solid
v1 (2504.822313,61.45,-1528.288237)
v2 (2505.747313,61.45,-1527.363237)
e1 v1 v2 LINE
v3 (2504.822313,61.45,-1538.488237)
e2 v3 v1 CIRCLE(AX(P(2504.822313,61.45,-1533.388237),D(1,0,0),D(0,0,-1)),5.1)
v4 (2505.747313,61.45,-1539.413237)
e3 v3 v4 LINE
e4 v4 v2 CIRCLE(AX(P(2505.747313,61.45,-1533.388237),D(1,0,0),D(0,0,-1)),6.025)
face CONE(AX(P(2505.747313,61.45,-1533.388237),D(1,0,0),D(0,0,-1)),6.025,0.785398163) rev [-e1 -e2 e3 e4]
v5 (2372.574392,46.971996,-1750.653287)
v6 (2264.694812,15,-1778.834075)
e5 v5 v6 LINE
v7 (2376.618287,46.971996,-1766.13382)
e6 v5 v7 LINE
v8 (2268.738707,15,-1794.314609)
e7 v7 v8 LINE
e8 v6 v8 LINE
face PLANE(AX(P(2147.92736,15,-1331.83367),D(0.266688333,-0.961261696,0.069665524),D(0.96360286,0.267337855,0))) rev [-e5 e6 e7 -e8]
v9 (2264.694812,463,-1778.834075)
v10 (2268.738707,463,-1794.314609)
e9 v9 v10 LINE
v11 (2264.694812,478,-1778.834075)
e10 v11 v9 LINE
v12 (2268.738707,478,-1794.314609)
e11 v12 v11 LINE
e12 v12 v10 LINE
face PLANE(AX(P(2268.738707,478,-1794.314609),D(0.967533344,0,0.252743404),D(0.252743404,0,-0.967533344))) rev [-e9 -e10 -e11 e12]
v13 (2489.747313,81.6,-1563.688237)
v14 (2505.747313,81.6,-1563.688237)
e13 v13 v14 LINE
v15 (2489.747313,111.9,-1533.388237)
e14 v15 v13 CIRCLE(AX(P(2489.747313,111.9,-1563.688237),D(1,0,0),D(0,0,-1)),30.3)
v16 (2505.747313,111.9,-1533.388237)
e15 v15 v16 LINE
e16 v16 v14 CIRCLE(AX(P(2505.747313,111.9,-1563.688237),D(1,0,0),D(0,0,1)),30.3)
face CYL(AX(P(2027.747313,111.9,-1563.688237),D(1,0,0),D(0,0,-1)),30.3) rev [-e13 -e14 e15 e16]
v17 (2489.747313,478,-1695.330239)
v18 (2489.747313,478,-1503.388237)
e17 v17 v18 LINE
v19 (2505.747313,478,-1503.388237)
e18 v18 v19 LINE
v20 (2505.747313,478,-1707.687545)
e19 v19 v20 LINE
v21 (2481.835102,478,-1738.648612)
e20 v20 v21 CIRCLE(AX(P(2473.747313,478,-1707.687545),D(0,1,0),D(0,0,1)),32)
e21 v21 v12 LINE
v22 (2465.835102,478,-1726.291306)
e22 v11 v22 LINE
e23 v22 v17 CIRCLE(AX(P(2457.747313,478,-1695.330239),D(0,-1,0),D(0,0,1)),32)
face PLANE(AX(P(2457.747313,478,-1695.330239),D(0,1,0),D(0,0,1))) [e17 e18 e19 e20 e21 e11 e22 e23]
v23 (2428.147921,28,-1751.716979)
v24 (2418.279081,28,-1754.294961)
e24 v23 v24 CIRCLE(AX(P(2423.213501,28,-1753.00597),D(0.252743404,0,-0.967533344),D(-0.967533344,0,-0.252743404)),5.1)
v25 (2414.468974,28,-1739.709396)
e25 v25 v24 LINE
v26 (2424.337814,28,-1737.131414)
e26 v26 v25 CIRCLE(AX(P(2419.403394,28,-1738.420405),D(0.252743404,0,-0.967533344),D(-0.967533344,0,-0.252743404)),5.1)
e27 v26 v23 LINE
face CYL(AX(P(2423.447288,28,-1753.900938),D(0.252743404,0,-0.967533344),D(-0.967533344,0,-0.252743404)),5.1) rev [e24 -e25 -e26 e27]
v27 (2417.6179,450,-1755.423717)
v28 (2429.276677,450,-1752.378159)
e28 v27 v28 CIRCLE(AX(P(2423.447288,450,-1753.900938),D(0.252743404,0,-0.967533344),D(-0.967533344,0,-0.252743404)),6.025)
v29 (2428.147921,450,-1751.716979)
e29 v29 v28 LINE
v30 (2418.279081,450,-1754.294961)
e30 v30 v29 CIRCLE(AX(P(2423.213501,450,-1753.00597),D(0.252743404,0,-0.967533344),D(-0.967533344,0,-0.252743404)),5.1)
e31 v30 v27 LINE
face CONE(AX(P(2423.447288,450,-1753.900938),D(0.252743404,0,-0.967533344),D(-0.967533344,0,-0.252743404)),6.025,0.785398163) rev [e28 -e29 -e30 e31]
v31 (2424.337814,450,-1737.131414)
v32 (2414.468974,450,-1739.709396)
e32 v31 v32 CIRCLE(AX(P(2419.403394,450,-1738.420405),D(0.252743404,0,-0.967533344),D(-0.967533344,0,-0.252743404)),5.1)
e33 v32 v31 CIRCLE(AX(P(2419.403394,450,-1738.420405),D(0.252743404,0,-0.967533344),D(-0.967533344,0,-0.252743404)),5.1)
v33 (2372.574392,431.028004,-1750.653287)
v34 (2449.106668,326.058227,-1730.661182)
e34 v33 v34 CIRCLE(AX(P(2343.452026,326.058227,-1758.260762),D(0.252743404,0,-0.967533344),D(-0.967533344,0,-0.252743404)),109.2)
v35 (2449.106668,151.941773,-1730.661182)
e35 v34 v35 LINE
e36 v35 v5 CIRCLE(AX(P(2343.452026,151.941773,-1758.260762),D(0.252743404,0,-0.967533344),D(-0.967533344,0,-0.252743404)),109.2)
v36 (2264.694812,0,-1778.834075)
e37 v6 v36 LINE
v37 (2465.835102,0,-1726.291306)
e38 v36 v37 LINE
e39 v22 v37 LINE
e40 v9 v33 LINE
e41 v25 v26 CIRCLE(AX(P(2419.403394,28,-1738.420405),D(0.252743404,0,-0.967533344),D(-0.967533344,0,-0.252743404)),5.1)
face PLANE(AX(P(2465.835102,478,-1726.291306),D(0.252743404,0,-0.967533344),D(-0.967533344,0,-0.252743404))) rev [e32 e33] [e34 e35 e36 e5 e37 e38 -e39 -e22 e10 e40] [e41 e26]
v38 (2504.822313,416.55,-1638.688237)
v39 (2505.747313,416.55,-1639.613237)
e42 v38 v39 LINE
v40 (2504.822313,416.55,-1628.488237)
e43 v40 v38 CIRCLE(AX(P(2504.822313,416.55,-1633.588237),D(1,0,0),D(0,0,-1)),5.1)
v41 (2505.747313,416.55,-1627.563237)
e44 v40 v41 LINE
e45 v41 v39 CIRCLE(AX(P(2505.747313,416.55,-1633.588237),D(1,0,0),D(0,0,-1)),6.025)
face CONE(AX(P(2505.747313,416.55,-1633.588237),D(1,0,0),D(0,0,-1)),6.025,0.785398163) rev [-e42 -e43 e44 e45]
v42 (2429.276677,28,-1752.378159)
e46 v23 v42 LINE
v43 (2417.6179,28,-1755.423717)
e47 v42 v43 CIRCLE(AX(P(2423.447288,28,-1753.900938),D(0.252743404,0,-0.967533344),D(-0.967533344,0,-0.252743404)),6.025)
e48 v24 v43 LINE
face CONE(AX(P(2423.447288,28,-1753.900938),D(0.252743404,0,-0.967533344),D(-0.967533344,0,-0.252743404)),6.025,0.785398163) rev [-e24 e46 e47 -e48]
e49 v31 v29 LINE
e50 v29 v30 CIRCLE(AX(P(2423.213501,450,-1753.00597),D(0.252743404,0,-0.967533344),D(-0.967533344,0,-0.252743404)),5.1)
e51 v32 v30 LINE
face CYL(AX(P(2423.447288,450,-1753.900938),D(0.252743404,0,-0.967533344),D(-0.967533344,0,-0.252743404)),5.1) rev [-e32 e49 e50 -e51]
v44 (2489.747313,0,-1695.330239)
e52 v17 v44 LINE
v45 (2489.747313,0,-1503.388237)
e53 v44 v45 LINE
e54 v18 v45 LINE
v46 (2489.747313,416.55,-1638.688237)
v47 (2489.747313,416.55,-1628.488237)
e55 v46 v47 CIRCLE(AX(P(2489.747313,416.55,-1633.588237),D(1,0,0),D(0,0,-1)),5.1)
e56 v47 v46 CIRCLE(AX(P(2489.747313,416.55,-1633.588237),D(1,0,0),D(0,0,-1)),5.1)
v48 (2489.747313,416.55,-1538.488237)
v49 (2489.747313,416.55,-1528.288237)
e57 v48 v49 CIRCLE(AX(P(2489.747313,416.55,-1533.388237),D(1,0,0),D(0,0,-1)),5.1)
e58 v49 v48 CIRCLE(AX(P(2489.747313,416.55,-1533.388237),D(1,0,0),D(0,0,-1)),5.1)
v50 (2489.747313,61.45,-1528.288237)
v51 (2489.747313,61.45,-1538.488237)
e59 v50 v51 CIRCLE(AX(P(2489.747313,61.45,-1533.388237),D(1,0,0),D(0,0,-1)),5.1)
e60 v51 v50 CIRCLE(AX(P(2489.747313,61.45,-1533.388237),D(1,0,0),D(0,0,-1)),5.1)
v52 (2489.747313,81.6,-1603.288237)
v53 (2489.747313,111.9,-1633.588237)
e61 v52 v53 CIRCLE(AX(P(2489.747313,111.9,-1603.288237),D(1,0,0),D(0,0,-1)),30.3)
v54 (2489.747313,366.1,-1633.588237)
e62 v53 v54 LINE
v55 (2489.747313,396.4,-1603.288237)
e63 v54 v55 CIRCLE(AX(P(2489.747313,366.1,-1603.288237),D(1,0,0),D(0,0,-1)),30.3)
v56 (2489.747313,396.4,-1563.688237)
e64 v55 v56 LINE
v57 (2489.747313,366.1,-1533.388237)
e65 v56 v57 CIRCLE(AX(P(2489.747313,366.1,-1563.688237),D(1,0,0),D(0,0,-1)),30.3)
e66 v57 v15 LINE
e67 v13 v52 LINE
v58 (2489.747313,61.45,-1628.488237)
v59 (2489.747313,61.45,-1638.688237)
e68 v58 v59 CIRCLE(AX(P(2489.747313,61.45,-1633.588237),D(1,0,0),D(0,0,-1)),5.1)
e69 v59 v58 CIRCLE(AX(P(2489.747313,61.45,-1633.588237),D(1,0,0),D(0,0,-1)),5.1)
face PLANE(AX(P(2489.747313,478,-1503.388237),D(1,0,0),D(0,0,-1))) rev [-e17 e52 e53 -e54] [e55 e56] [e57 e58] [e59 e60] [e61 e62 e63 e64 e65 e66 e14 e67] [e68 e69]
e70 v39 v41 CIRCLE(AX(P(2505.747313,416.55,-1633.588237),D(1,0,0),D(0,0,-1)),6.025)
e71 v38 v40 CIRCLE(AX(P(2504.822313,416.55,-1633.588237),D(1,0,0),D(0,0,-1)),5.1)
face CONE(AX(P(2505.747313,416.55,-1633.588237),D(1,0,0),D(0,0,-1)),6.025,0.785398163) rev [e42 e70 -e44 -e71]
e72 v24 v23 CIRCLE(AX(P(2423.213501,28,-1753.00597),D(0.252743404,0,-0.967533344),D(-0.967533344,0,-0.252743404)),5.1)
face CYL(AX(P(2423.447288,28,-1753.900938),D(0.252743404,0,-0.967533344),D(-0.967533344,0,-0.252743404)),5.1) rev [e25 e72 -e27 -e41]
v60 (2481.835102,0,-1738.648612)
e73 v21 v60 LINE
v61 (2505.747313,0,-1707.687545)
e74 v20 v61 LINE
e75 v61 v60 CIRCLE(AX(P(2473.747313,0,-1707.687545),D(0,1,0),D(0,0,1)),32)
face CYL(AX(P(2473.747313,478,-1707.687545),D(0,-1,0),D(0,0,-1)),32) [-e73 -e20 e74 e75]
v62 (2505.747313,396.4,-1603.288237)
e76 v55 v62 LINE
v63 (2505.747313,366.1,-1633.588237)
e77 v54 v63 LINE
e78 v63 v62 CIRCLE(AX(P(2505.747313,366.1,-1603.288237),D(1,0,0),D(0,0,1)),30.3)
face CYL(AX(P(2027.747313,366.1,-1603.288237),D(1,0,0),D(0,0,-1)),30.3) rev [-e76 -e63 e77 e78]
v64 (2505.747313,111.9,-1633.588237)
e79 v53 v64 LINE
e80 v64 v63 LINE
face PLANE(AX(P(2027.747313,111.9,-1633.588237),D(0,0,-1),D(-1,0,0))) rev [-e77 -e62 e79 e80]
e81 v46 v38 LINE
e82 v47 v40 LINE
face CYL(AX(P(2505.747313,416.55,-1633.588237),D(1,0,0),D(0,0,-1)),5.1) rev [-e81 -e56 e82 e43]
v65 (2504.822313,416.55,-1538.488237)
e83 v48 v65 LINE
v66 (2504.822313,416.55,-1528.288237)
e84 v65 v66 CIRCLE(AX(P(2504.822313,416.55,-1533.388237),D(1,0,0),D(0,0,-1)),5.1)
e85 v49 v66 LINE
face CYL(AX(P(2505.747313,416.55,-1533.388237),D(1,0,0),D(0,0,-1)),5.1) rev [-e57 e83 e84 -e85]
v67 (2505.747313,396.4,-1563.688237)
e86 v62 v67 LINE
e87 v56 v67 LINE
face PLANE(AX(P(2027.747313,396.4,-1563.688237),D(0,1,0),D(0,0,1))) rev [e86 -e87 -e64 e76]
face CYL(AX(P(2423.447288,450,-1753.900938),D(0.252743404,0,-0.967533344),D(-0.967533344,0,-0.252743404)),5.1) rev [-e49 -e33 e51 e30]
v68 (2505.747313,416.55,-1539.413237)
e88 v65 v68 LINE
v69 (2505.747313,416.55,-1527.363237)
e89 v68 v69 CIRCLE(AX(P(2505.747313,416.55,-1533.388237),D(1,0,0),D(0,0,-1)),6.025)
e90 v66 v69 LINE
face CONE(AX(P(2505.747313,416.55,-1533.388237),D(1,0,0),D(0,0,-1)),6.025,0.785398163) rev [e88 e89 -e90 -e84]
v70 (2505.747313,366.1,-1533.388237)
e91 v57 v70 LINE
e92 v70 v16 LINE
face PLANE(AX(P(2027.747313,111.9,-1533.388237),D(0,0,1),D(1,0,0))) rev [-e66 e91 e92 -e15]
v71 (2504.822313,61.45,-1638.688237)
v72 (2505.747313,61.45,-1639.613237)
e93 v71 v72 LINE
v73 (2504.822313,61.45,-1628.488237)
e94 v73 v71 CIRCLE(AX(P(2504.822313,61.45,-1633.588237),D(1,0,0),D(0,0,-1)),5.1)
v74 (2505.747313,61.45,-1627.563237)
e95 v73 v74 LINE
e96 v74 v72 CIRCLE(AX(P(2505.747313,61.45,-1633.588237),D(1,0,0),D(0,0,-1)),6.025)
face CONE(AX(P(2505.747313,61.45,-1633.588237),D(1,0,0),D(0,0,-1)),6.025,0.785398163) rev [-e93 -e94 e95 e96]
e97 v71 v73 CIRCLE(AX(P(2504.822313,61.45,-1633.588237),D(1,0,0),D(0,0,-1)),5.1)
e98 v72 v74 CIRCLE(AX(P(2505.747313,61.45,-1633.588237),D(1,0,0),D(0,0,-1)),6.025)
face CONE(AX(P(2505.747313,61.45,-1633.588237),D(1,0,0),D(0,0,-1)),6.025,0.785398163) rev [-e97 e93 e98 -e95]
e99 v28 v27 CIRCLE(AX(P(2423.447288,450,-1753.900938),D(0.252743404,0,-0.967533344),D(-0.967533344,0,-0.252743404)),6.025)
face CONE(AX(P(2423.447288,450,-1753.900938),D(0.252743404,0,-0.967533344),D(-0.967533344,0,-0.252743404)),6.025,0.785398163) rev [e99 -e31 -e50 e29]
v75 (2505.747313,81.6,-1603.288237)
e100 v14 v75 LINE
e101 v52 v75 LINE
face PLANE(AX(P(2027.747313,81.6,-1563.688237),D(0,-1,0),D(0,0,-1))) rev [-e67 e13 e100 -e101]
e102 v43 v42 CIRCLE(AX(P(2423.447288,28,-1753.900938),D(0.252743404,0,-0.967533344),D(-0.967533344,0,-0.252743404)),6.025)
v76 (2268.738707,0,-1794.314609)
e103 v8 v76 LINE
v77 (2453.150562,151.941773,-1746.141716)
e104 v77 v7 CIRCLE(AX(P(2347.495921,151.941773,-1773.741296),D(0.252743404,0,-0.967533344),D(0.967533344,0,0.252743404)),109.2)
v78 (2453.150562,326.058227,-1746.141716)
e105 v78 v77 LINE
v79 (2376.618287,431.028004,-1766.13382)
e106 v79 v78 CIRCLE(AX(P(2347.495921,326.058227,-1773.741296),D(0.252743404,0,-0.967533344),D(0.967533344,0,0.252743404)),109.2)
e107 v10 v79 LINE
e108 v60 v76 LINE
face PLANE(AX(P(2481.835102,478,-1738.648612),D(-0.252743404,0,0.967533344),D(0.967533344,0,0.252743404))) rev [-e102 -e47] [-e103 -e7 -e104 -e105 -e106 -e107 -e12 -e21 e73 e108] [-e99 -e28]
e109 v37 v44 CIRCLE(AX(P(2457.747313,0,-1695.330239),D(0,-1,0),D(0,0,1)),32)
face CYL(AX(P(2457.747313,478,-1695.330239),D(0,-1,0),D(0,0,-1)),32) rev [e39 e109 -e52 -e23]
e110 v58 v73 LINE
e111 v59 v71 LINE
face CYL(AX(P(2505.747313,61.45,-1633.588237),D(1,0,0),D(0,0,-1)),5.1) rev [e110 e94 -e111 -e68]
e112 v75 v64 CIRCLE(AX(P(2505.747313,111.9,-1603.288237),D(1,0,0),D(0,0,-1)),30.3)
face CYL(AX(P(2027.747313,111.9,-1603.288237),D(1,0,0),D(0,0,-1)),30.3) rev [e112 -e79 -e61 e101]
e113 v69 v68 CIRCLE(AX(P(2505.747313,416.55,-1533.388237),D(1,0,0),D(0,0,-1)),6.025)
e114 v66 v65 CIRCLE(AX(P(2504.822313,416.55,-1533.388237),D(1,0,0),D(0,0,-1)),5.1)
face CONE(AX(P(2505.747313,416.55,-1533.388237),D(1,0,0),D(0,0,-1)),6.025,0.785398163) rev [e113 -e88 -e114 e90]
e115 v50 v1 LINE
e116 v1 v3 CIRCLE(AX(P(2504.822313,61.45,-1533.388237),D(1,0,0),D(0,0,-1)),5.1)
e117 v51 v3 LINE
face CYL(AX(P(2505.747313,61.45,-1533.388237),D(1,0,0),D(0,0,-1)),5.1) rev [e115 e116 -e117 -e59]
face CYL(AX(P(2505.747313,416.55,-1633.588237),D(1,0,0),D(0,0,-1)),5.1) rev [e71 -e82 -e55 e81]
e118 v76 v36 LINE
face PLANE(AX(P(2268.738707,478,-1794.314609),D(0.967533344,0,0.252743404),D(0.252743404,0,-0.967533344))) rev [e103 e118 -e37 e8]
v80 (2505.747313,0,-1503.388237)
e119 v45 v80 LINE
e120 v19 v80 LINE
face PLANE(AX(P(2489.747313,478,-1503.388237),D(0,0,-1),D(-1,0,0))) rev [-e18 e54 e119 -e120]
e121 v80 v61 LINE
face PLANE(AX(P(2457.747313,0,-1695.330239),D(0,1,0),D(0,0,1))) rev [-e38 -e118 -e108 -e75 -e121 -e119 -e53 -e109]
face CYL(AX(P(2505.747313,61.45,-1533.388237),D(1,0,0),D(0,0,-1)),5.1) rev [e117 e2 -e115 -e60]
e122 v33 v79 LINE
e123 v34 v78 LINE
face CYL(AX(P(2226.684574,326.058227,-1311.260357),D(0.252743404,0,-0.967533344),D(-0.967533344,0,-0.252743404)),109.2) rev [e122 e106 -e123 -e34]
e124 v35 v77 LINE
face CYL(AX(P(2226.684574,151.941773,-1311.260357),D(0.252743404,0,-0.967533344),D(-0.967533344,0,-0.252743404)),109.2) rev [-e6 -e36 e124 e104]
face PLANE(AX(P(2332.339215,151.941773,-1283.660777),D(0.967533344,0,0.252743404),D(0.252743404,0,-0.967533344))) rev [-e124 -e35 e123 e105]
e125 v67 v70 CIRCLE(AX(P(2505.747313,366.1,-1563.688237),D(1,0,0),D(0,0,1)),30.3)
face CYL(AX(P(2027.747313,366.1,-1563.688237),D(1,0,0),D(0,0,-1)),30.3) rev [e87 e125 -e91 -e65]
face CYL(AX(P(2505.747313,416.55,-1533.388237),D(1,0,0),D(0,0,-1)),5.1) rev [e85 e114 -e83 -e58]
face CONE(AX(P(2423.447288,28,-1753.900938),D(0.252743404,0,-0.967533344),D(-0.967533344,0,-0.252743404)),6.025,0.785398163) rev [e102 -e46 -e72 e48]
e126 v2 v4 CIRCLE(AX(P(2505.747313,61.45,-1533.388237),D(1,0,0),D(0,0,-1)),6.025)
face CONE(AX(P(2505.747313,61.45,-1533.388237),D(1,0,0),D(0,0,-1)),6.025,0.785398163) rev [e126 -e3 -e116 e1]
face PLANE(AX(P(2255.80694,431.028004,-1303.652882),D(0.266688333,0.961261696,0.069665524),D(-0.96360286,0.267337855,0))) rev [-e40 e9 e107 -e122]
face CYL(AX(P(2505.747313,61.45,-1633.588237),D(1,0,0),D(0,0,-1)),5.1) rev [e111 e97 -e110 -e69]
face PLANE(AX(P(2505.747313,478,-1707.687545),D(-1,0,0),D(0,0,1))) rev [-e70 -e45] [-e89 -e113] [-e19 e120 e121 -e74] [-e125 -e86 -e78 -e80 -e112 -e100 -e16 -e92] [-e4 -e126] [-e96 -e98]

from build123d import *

# Parameters (mm, degrees)
BOSS_EXTRUDE1_DEPTH          = 478
CUT_EXTRUDE1_DEPTH           = 478
M12_TAPPED_HOLE1_D           = 10.2
M12_TAPPED_HOLE1_CSINK_D     = 12.05
M12_TAPPED_HOLE1_CSINK_ANGLE = 90
CUT_EXTRUDE2_DEPTH           = 478
M12_TAPPED_HOLE2_D           = 10.2
M12_TAPPED_HOLE2_CSINK_D     = 12.05
M12_TAPPED_HOLE2_CSINK_ANGLE = 90


with BuildPart() as part:
    # Sketch1 → Boss-Extrude1 (new body)
    with BuildSketch(Plane(origin=(0, 0, 0), x_dir=(1, 0, 0), z_dir=(0, 1, 0))):
        with BuildLine():
            Line((2489.747313266, 1503.388237), (2505.747313266, 1503.388237))
            Line((2505.747313266, 1503.388237), (2505.747313266, 1707.687544505))
            ThreePointArc((2505.747313266, 1707.687544505), (2499.07328063, 1727.247589931), (2481.835102198, 1738.648611511))
            Line((2481.835102198, 1738.648611511), (2268.738706702, 1794.314608702))
            Line((2268.738706702, 1794.314608702), (2264.694812236, 1778.834075199))
            Line((2264.694812236, 1778.834075199), (2465.835102198, 1726.291305576))
            ThreePointArc((2465.835102198, 1726.291305576), (2483.07328063, 1714.890283996), (2489.747313266, 1695.33023857))
            Line((2489.747313266, 1695.33023857), (2489.747313266, 1503.388237))
        make_face()
    extrude(amount=BOSS_EXTRUDE1_DEPTH)

    # Sketch2 → Cut-Extrude1 (cut)
    with BuildSketch(Plane(origin=(2505.747313266, 0, 0), x_dir=(0, 0, -1), z_dir=(1, 0, 0))):
        with BuildLine():
            Line((1563.688237, 81.6), (1603.288237, 81.6))
            ThreePointArc((1603.288237, 81.6), (1624.71357247, 90.47466453), (1633.588237, 111.9))
            Line((1633.588237, 111.9), (1633.588237, 366.1))
            ThreePointArc((1633.588237, 366.1), (1624.71357247, 387.52533547), (1603.288237, 396.4))
            Line((1603.288237, 396.4), (1563.688237, 396.4))
            ThreePointArc((1563.688237, 396.4), (1542.26290153, 387.52533547), (1533.388237, 366.1))
            Line((1533.388237, 366.1), (1533.388237, 111.9))
            ThreePointArc((1533.388237, 111.9), (1542.26290153, 90.47466453), (1563.688237, 81.6))
        make_face()
    extrude(amount=-CUT_EXTRUDE1_DEPTH, mode=Mode.SUBTRACT)

    # M12 Tapped Hole1 (through all)
    with Locations(Plane(origin=(2505.747313266, 0, 0), x_dir=(0, 0, -1), z_dir=(1, 0, 0))):
        with Locations((1633.588237, 416.55), (1533.388237, 61.45), (1533.388237, 416.55), (1633.588237, 61.45)):
            CounterSinkHole(M12_TAPPED_HOLE1_D / 2, M12_TAPPED_HOLE1_CSINK_D / 2, counter_sink_angle=M12_TAPPED_HOLE1_CSINK_ANGLE)

    # Sketch7 → Cut-Extrude2 (cut)
    with BuildSketch(Plane(origin=(583.702793267, 0, -2234.487255477), x_dir=(-0.9675333439556839, 0, -0.2527434041353648), z_dir=(0.2527434041353648, 0, -0.967533343955684))):
        with BuildLine():
            Line((-1741.579165164, 463), (-1741.579165164, 15))
            Line((-1741.579165164, 15), (-1853.078764419, 46.9719956))
            ThreePointArc((-1853.078764419, 46.9719956), (-1910.190162861, 86.223572269), (-1932.179165164, 151.941772797))
            Line((-1932.179165164, 151.941772797), (-1932.179165164, 326.058227203))
            ThreePointArc((-1932.179165164, 326.058227203), (-1910.190162861, 391.776427731), (-1853.078764419, 431.0280044))
            Line((-1853.078764419, 431.0280044), (-1741.579165164, 463))
        make_face()
    extrude(amount=-CUT_EXTRUDE2_DEPTH, mode=Mode.SUBTRACT)

    # M12 Tapped Hole2 (through all)
    with Locations(Plane(origin=(583.702793267, 0, -2234.487255477), x_dir=(-0.9675333439556839, 0, -0.2527434041353648), z_dir=(0.2527434041353648, 0, -0.967533343955684))):
        with Locations((-1901.479165164, 450), (-1901.479165164, 28)):
            CounterSinkHole(M12_TAPPED_HOLE2_D / 2, M12_TAPPED_HOLE2_CSINK_D / 2, counter_sink_angle=M12_TAPPED_HOLE2_CSINK_ANGLE)


solid = part.part
